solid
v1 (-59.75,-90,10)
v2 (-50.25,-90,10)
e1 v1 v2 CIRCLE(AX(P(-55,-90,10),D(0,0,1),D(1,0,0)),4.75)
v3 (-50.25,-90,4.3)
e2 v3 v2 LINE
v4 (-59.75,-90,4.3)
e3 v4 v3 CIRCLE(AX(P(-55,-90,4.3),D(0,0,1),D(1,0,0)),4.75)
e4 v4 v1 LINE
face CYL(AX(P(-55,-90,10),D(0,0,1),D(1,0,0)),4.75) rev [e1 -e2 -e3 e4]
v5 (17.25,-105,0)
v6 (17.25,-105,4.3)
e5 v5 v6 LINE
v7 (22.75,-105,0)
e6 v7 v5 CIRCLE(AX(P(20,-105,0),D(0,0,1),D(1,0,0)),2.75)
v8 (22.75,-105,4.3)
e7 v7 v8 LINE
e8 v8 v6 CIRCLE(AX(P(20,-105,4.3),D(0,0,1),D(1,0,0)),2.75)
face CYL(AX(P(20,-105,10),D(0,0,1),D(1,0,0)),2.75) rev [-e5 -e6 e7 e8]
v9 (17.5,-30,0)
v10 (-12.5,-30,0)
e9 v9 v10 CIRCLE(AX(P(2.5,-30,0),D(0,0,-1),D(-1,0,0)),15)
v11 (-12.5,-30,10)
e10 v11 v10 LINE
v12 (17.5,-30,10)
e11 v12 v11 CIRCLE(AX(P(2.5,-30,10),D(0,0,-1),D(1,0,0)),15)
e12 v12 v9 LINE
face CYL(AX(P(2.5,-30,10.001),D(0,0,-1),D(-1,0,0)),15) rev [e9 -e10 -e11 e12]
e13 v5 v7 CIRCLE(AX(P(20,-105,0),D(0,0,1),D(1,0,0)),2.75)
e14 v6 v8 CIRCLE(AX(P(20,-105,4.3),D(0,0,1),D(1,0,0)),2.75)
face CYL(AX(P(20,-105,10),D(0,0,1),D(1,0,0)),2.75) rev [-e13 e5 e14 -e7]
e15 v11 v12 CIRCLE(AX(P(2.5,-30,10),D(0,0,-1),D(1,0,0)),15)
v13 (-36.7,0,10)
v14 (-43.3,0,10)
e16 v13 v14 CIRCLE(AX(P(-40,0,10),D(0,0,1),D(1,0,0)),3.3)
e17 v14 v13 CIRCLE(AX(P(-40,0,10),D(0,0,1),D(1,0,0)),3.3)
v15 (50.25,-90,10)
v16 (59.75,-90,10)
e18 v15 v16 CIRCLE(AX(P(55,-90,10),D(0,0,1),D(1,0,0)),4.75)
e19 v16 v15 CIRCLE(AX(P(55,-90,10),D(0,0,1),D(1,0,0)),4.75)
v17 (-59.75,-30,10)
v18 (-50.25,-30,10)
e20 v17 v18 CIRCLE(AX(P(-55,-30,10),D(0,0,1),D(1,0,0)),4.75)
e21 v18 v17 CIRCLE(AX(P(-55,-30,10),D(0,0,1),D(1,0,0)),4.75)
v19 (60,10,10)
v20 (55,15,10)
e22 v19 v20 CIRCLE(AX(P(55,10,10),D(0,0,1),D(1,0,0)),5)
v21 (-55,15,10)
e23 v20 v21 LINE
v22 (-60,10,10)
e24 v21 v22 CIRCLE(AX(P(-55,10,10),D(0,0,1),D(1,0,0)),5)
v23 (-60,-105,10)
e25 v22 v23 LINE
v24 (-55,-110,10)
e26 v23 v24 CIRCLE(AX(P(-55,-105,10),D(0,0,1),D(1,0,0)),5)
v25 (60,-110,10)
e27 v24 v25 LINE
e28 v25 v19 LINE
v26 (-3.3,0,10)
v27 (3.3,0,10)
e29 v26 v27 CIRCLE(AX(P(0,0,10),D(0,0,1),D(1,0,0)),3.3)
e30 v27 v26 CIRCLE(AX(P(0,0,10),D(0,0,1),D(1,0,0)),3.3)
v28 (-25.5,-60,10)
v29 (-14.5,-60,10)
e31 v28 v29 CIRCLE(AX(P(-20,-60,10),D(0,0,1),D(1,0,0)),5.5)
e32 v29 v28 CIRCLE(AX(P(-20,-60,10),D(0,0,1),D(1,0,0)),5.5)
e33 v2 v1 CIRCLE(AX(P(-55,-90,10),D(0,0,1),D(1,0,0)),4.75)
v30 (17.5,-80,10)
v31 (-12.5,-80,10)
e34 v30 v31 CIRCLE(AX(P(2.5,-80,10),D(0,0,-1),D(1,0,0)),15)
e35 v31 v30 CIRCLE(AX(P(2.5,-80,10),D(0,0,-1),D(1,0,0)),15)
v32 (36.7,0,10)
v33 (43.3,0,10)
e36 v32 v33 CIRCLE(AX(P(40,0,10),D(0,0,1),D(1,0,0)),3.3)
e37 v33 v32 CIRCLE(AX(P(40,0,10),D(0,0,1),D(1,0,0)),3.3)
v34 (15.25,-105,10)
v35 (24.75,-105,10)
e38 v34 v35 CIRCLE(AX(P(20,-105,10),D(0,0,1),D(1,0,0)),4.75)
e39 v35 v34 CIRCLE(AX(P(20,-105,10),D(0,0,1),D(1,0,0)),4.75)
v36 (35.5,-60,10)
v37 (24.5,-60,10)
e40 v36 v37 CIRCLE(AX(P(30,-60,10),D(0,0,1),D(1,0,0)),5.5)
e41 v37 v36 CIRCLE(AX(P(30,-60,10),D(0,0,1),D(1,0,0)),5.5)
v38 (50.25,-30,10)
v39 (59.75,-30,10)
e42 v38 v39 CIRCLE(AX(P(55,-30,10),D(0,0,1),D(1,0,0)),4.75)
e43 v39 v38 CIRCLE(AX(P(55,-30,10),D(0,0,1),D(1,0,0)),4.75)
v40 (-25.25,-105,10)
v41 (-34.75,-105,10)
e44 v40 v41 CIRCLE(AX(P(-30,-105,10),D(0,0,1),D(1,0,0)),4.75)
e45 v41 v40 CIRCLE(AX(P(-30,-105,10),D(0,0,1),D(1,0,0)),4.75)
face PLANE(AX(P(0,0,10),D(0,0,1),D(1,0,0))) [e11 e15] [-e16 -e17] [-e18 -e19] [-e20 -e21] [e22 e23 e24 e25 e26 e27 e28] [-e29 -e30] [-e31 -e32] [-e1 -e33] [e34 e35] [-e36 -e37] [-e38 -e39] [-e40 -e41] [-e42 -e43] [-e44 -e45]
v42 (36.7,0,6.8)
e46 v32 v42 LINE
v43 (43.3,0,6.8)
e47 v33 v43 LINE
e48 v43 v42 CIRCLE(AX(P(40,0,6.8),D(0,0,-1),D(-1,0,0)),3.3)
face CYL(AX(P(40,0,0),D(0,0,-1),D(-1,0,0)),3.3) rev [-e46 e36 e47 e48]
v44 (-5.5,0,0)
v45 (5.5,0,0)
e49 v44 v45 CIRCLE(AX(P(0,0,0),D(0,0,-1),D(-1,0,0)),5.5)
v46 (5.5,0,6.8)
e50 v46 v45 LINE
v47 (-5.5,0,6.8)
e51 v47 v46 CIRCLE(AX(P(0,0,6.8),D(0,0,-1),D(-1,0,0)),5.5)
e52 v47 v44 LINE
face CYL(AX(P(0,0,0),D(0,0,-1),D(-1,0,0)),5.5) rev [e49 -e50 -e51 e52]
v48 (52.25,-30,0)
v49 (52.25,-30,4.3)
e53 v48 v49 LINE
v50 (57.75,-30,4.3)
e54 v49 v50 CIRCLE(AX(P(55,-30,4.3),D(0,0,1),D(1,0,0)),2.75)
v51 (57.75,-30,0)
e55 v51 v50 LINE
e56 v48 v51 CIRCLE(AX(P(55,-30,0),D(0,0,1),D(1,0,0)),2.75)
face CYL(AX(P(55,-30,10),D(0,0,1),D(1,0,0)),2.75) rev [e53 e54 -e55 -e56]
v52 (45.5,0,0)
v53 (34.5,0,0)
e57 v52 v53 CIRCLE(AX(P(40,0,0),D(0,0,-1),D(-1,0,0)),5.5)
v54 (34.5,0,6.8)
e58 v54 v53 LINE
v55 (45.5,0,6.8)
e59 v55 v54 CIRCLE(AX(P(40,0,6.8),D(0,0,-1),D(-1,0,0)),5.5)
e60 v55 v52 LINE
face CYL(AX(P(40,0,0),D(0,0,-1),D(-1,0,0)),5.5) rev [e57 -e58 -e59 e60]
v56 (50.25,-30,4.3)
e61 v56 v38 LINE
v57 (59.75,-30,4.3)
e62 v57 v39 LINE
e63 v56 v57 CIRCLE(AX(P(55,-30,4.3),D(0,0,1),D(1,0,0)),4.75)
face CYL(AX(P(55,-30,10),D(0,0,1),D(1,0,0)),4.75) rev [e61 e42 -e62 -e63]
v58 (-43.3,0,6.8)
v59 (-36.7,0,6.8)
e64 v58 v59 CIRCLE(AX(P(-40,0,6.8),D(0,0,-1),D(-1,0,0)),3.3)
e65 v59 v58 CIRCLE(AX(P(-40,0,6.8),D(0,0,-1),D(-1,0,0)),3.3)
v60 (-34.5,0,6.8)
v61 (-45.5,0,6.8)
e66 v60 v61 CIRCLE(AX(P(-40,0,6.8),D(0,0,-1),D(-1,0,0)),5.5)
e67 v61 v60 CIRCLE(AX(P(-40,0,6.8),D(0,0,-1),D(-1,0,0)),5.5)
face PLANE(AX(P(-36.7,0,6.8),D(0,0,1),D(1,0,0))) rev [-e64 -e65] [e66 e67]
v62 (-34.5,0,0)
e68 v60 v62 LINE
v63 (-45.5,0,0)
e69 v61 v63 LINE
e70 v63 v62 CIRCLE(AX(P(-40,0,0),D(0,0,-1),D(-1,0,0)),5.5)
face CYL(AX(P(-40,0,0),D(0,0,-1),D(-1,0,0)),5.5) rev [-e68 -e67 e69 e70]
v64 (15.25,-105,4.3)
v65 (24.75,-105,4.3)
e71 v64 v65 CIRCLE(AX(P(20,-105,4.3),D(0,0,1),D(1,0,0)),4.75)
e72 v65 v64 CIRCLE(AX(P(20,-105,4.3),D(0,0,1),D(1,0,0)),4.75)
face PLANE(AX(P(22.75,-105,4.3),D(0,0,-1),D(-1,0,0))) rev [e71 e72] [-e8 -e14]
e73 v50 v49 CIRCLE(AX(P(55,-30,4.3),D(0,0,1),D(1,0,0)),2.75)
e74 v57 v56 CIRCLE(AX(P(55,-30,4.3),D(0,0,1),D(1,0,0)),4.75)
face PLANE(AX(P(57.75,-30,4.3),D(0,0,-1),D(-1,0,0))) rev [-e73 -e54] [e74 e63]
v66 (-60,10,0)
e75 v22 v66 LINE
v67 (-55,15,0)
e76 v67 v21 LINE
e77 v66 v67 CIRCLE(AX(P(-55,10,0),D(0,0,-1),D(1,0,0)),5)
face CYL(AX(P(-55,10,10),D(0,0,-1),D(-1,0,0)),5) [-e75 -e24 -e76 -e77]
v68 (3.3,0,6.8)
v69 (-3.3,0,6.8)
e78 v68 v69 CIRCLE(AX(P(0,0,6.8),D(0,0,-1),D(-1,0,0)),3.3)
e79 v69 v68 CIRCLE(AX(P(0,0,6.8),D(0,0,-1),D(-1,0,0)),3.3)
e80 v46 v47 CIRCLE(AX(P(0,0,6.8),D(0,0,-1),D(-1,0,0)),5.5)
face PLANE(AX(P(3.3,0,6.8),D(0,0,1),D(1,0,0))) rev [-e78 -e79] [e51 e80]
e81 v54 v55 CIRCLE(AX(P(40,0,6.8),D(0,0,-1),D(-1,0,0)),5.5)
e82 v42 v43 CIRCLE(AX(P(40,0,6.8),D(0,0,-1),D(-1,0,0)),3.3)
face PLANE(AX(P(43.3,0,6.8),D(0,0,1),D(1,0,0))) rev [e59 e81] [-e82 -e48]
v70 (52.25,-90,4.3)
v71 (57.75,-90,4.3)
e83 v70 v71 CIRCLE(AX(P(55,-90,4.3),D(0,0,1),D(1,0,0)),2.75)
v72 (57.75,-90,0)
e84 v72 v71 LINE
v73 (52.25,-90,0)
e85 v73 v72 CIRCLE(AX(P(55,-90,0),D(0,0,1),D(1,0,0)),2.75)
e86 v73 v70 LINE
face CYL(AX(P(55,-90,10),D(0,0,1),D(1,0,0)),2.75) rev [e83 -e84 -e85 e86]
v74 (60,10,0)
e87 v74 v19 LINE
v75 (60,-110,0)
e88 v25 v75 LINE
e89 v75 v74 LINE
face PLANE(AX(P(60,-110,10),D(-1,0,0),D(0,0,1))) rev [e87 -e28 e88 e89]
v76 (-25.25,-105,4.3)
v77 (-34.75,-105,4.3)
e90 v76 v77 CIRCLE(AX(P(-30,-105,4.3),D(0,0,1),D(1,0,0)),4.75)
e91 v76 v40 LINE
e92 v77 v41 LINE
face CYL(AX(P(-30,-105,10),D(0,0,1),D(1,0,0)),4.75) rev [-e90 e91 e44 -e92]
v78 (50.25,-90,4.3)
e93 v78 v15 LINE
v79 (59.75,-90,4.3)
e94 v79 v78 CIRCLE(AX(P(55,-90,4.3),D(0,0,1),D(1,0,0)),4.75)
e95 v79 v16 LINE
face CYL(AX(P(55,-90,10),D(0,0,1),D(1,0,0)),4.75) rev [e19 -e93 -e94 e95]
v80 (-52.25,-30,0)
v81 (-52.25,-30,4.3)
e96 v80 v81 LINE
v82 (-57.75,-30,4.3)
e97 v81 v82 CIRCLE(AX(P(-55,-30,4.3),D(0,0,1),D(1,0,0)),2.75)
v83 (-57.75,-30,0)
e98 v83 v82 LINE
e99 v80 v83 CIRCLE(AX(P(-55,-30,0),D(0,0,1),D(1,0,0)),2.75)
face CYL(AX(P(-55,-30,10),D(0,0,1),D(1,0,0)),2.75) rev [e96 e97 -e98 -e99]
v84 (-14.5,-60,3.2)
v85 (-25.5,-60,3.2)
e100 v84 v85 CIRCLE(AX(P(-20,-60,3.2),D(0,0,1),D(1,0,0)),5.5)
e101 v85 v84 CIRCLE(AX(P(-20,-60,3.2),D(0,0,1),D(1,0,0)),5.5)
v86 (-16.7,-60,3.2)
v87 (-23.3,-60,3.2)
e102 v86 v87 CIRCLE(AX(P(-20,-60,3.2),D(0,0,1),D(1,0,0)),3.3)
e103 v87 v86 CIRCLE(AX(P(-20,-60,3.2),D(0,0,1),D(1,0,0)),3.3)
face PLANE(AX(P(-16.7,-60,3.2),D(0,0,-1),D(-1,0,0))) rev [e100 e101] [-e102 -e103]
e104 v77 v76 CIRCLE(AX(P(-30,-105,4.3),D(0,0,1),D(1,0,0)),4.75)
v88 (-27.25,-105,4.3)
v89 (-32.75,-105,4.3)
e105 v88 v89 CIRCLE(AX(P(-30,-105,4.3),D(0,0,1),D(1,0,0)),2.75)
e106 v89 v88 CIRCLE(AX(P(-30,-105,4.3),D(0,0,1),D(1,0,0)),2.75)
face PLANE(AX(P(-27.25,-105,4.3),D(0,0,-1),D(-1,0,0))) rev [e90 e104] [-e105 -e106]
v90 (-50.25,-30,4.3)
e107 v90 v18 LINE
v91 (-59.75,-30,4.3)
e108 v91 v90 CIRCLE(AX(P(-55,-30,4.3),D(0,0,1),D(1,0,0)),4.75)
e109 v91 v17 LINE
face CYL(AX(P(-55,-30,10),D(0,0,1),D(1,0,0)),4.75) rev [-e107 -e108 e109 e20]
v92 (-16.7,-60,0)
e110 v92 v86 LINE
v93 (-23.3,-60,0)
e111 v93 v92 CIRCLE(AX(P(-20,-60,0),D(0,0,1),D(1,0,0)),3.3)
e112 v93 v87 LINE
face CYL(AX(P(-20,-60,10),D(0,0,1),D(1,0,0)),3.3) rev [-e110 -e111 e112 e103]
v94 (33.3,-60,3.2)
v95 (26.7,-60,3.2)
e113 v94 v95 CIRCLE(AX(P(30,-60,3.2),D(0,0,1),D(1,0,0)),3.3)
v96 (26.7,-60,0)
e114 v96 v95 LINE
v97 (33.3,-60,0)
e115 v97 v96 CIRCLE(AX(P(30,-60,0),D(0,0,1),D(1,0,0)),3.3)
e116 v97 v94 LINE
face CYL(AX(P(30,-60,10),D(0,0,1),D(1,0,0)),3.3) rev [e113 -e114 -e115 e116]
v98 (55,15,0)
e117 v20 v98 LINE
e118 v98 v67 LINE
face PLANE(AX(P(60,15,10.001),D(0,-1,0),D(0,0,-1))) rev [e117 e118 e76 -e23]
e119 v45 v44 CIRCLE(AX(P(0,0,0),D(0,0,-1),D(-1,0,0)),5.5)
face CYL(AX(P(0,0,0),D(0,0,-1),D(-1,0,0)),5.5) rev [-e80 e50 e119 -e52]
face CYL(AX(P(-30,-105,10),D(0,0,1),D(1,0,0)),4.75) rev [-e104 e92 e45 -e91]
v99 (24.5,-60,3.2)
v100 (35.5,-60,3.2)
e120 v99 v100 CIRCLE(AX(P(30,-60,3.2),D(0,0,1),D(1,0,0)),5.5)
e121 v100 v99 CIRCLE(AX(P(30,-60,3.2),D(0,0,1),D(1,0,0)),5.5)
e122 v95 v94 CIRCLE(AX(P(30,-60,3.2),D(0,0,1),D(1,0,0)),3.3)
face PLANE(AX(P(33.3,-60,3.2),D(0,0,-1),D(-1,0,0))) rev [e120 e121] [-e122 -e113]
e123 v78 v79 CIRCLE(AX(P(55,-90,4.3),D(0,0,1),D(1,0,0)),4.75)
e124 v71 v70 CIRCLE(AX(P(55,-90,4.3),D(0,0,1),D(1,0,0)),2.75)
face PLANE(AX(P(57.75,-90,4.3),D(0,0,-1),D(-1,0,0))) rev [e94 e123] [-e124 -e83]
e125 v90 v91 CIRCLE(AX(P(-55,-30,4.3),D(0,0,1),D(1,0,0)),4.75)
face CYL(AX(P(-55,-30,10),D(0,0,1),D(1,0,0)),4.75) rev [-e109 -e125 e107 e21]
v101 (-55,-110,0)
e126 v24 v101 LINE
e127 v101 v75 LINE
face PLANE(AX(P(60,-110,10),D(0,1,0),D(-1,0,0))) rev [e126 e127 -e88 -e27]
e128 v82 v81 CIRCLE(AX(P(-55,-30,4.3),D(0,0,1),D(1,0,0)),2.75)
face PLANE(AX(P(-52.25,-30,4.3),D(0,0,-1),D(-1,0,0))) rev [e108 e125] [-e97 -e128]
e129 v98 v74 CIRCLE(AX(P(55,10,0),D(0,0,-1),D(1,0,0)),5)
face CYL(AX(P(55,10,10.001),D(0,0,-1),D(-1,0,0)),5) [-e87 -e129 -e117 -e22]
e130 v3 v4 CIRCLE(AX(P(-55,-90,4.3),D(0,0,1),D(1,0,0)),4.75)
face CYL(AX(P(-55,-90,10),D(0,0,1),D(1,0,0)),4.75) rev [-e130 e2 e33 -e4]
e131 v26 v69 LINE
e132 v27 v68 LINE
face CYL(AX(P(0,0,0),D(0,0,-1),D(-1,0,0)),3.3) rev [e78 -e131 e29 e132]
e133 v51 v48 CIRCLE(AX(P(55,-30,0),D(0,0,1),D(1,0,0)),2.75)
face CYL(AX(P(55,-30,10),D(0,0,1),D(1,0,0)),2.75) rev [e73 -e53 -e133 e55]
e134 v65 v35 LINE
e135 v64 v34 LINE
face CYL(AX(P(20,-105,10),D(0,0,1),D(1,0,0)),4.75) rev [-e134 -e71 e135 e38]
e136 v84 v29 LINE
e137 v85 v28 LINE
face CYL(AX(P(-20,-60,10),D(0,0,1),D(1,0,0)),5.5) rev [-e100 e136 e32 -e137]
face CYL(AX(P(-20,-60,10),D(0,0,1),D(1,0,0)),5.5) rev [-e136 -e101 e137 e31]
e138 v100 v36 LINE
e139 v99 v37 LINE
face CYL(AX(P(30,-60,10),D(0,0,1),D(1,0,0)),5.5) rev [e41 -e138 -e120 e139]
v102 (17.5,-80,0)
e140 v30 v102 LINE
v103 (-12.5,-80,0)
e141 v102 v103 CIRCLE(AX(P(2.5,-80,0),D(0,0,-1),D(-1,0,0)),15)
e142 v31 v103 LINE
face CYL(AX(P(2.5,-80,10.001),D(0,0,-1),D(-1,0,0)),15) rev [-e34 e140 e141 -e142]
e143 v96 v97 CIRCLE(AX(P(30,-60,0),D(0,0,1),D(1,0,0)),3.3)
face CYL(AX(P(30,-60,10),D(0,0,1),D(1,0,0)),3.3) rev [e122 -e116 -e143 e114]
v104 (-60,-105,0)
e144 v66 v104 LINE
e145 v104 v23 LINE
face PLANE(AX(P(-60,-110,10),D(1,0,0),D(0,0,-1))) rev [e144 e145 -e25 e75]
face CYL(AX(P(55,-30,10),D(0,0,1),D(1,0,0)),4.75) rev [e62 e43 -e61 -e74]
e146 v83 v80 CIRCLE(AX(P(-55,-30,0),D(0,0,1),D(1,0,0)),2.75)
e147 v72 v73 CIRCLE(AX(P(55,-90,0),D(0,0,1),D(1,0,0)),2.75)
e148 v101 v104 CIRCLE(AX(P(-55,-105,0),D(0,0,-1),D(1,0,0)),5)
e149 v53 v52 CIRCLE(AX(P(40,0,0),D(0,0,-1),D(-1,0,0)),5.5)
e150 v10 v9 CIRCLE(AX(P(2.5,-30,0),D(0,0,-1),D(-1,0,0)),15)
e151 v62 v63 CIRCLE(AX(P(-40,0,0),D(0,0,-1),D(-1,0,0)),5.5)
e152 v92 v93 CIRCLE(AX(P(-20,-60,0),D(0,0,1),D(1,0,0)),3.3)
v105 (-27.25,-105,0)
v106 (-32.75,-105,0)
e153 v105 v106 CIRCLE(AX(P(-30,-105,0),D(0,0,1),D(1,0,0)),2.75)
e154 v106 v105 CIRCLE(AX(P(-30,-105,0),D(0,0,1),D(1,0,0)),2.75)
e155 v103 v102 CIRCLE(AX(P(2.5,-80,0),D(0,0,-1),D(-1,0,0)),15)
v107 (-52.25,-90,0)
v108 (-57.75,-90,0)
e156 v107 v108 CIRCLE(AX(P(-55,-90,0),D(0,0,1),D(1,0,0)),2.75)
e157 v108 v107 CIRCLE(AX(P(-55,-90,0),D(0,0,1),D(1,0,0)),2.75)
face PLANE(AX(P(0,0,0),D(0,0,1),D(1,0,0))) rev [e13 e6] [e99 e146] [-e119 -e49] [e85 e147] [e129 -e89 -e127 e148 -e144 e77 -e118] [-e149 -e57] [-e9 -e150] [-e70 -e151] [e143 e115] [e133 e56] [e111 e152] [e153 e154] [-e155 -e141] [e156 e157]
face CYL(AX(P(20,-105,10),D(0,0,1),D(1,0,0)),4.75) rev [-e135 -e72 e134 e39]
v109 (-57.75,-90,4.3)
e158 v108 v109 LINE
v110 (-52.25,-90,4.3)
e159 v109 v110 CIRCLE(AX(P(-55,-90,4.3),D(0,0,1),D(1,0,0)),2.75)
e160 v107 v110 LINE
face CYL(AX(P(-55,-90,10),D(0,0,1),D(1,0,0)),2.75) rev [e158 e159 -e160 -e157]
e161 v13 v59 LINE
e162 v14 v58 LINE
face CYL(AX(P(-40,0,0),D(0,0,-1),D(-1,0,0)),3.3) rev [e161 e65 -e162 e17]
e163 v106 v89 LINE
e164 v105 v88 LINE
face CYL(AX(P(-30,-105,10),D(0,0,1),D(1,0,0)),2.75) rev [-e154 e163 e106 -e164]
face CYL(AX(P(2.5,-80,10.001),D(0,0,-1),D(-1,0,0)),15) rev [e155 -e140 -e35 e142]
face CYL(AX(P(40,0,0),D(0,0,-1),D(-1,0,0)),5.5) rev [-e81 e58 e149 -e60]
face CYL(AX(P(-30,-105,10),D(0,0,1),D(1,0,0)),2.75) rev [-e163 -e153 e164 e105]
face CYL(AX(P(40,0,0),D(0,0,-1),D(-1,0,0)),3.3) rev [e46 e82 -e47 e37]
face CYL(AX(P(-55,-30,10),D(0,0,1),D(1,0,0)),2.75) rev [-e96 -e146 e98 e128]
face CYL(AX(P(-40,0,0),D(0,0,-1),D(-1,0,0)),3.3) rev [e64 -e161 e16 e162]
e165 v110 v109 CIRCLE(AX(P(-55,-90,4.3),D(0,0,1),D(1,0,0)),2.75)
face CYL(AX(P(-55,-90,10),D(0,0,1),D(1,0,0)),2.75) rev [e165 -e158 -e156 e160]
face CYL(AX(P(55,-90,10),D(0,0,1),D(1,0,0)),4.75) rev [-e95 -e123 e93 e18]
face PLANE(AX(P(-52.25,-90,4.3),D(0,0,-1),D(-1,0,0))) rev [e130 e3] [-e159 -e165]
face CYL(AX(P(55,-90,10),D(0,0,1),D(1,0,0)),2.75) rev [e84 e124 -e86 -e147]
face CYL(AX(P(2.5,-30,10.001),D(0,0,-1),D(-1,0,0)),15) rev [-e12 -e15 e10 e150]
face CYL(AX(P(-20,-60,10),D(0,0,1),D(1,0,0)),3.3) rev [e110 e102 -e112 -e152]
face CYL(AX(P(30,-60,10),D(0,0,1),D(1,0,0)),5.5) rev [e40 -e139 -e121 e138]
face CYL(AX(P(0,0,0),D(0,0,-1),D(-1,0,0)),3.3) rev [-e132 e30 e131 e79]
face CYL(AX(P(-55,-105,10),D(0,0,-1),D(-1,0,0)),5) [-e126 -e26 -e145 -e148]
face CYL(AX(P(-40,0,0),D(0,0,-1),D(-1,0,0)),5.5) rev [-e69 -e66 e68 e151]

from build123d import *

# Parameters (mm, degrees)
SKETCH_1_W                = 120
SKETCH_1_H                = 220
EXTRUDE_1_DEPTH           = 10
HOLE_WIZARD_2_D           = 5.5
HOLE_WIZARD_2_CBORE_D     = 9.5
HOLE_WIZARD_2_CBORE_DEPTH = 5.7
HOLE_WIZARD_3_D           = 6.6
HOLE_WIZARD_3_CBORE_D     = 11
HOLE_WIZARD_3_CBORE_DEPTH = 6.8
FILLET_1_R                = 5
CUT_EXTRUDE_1_REACH       = 127.698
SKETCH_11_W               = 120
SKETCH_11_H               = 95
HOLE_WIZARD_4_D           = 6.6
HOLE_WIZARD_4_CBORE_D     = 11
HOLE_WIZARD_4_CBORE_DEPTH = 6.8
FILLET_2_R                = 5
CUT_EXTRUDE_2_REACH       = 127.698
SKETCH_14_R               = 15
HOLE_WIZARD_5_D           = 5.5
HOLE_WIZARD_5_DEPTH       = 20.4
HOLE_WIZARD_5_CBORE_D     = 9.5
HOLE_WIZARD_5_CBORE_DEPTH = 5.7
HOLE_WIZARD_5_TIP         = 1.652366702


with BuildPart() as part:
    # 草图1 → 凸台-拉伸1 (new body)
    with BuildSketch(Plane.XY):
        Rectangle(SKETCH_1_W, SKETCH_1_H)
    extrude(amount=EXTRUDE_1_DEPTH)

    # 打孔尺寸(%根据)内六角圆柱头螺钉的类型2 (through all)
    with Locations(Plane.XY.offset(10)):
        with Locations((-55, -30), (-55, -90)):
            hole_wizard_2 = CounterBoreHole(HOLE_WIZARD_2_D / 2, HOLE_WIZARD_2_CBORE_D / 2, HOLE_WIZARD_2_CBORE_DEPTH)

    # 打孔尺寸(%根据)内六角圆柱头螺钉的类型3 (through all)
    with Locations(Plane.XY.offset(10)):
        with Locations((-20, -60), (30, -60)):
            CounterBoreHole(HOLE_WIZARD_3_D / 2, HOLE_WIZARD_3_CBORE_D / 2, HOLE_WIZARD_3_CBORE_DEPTH)

    # 圆角1
    fillet_1_edges = [part.edges().sort_by_distance(p)[0] for p in [
        (-60, 110, 5),
        (-60, -110, 5),
    ]]
    fillet(fillet_1_edges, radius=FILLET_1_R)

    # 草图11 → 切除-拉伸1 (cut, up to next)
    with BuildSketch(Plane(origin=(0, 0, 0), x_dir=(-1, 0, 0), z_dir=(0, 0, -1)), mode=Mode.PRIVATE) as cut_extrude_1_sk1:
        with Locations((0, 62.5)):
            Rectangle(SKETCH_11_W, SKETCH_11_H)
    cut_extrude_1_tool1 = extrude(cut_extrude_1_sk1.sketch, amount=-CUT_EXTRUDE_1_REACH, mode=Mode.PRIVATE) & part.part
    add(cut_extrude_1_tool1.solids().sort_by_distance((0, 62.5, 0))[0], mode=Mode.SUBTRACT)

    # 打孔尺寸(%根据)内六角圆柱头螺钉的类型4 (through all)
    with Locations(Plane(origin=(0, 0, 0), x_dir=(-1, 0, 0), z_dir=(0, 0, -1))):
        with Locations((-40, 0), (0, 0), (40, 0)):
            CounterBoreHole(HOLE_WIZARD_4_D / 2, HOLE_WIZARD_4_CBORE_D / 2, HOLE_WIZARD_4_CBORE_DEPTH)

    # 圆角2
    fillet_2_edges = [part.edges().sort_by_distance(p)[0] for p in [
        (60, 15, 5),
        (-60, 15, 5),
    ]]
    fillet(fillet_2_edges, radius=FILLET_2_R)

    # 草图14 → 切除-拉伸2 (cut, up to next)
    with BuildSketch(Plane(origin=(0, 0, 0), x_dir=(-1, 0, 0), z_dir=(0, 0, -1)), mode=Mode.PRIVATE) as cut_extrude_2_sk1:
        with Locations((-2.5, -30)):
            Circle(SKETCH_14_R)
    cut_extrude_2_tool1 = extrude(cut_extrude_2_sk1.sketch, amount=-CUT_EXTRUDE_2_REACH, mode=Mode.PRIVATE) & part.part
    # 草图14 → 切除-拉伸2 (cut, up to next)
    with BuildSketch(Plane(origin=(0, 0, 0), x_dir=(-1, 0, 0), z_dir=(0, 0, -1)), mode=Mode.PRIVATE) as cut_extrude_2_sk2:
        with Locations((-2.5, -80)):
            Circle(SKETCH_14_R)
    cut_extrude_2_tool2 = extrude(cut_extrude_2_sk2.sketch, amount=-CUT_EXTRUDE_2_REACH, mode=Mode.PRIVATE) & part.part
    add(cut_extrude_2_tool1.solids().sort_by_distance((2.5, -30, 0))[0], mode=Mode.SUBTRACT)
    add(cut_extrude_2_tool2.solids().sort_by_distance((2.5, -80, 0))[0], mode=Mode.SUBTRACT)

    # 镜向1: 打孔尺寸(%根据)内六角圆柱头螺钉的类型2 across plane
    add(hole_wizard_2.mirror(Plane(origin=(0, 0, 0), x_dir=(0, 0, 1), z_dir=(1, 0, 0))), mode=Mode.SUBTRACT)

    # 打孔尺寸(%根据)内六角圆柱头螺钉的类型5
    with Locations(Plane.XY.offset(10)):
        with Locations((20, -105), (-30, -105)):
            CounterBoreHole(HOLE_WIZARD_5_D / 2, HOLE_WIZARD_5_CBORE_D / 2, HOLE_WIZARD_5_CBORE_DEPTH, depth=HOLE_WIZARD_5_DEPTH)
            with Locations((0, 0, -(HOLE_WIZARD_5_DEPTH + HOLE_WIZARD_5_TIP / 2))):  # 118° drill point
                Cone(0, HOLE_WIZARD_5_D / 2, HOLE_WIZARD_5_TIP, mode=Mode.SUBTRACT)


solid = part.part
